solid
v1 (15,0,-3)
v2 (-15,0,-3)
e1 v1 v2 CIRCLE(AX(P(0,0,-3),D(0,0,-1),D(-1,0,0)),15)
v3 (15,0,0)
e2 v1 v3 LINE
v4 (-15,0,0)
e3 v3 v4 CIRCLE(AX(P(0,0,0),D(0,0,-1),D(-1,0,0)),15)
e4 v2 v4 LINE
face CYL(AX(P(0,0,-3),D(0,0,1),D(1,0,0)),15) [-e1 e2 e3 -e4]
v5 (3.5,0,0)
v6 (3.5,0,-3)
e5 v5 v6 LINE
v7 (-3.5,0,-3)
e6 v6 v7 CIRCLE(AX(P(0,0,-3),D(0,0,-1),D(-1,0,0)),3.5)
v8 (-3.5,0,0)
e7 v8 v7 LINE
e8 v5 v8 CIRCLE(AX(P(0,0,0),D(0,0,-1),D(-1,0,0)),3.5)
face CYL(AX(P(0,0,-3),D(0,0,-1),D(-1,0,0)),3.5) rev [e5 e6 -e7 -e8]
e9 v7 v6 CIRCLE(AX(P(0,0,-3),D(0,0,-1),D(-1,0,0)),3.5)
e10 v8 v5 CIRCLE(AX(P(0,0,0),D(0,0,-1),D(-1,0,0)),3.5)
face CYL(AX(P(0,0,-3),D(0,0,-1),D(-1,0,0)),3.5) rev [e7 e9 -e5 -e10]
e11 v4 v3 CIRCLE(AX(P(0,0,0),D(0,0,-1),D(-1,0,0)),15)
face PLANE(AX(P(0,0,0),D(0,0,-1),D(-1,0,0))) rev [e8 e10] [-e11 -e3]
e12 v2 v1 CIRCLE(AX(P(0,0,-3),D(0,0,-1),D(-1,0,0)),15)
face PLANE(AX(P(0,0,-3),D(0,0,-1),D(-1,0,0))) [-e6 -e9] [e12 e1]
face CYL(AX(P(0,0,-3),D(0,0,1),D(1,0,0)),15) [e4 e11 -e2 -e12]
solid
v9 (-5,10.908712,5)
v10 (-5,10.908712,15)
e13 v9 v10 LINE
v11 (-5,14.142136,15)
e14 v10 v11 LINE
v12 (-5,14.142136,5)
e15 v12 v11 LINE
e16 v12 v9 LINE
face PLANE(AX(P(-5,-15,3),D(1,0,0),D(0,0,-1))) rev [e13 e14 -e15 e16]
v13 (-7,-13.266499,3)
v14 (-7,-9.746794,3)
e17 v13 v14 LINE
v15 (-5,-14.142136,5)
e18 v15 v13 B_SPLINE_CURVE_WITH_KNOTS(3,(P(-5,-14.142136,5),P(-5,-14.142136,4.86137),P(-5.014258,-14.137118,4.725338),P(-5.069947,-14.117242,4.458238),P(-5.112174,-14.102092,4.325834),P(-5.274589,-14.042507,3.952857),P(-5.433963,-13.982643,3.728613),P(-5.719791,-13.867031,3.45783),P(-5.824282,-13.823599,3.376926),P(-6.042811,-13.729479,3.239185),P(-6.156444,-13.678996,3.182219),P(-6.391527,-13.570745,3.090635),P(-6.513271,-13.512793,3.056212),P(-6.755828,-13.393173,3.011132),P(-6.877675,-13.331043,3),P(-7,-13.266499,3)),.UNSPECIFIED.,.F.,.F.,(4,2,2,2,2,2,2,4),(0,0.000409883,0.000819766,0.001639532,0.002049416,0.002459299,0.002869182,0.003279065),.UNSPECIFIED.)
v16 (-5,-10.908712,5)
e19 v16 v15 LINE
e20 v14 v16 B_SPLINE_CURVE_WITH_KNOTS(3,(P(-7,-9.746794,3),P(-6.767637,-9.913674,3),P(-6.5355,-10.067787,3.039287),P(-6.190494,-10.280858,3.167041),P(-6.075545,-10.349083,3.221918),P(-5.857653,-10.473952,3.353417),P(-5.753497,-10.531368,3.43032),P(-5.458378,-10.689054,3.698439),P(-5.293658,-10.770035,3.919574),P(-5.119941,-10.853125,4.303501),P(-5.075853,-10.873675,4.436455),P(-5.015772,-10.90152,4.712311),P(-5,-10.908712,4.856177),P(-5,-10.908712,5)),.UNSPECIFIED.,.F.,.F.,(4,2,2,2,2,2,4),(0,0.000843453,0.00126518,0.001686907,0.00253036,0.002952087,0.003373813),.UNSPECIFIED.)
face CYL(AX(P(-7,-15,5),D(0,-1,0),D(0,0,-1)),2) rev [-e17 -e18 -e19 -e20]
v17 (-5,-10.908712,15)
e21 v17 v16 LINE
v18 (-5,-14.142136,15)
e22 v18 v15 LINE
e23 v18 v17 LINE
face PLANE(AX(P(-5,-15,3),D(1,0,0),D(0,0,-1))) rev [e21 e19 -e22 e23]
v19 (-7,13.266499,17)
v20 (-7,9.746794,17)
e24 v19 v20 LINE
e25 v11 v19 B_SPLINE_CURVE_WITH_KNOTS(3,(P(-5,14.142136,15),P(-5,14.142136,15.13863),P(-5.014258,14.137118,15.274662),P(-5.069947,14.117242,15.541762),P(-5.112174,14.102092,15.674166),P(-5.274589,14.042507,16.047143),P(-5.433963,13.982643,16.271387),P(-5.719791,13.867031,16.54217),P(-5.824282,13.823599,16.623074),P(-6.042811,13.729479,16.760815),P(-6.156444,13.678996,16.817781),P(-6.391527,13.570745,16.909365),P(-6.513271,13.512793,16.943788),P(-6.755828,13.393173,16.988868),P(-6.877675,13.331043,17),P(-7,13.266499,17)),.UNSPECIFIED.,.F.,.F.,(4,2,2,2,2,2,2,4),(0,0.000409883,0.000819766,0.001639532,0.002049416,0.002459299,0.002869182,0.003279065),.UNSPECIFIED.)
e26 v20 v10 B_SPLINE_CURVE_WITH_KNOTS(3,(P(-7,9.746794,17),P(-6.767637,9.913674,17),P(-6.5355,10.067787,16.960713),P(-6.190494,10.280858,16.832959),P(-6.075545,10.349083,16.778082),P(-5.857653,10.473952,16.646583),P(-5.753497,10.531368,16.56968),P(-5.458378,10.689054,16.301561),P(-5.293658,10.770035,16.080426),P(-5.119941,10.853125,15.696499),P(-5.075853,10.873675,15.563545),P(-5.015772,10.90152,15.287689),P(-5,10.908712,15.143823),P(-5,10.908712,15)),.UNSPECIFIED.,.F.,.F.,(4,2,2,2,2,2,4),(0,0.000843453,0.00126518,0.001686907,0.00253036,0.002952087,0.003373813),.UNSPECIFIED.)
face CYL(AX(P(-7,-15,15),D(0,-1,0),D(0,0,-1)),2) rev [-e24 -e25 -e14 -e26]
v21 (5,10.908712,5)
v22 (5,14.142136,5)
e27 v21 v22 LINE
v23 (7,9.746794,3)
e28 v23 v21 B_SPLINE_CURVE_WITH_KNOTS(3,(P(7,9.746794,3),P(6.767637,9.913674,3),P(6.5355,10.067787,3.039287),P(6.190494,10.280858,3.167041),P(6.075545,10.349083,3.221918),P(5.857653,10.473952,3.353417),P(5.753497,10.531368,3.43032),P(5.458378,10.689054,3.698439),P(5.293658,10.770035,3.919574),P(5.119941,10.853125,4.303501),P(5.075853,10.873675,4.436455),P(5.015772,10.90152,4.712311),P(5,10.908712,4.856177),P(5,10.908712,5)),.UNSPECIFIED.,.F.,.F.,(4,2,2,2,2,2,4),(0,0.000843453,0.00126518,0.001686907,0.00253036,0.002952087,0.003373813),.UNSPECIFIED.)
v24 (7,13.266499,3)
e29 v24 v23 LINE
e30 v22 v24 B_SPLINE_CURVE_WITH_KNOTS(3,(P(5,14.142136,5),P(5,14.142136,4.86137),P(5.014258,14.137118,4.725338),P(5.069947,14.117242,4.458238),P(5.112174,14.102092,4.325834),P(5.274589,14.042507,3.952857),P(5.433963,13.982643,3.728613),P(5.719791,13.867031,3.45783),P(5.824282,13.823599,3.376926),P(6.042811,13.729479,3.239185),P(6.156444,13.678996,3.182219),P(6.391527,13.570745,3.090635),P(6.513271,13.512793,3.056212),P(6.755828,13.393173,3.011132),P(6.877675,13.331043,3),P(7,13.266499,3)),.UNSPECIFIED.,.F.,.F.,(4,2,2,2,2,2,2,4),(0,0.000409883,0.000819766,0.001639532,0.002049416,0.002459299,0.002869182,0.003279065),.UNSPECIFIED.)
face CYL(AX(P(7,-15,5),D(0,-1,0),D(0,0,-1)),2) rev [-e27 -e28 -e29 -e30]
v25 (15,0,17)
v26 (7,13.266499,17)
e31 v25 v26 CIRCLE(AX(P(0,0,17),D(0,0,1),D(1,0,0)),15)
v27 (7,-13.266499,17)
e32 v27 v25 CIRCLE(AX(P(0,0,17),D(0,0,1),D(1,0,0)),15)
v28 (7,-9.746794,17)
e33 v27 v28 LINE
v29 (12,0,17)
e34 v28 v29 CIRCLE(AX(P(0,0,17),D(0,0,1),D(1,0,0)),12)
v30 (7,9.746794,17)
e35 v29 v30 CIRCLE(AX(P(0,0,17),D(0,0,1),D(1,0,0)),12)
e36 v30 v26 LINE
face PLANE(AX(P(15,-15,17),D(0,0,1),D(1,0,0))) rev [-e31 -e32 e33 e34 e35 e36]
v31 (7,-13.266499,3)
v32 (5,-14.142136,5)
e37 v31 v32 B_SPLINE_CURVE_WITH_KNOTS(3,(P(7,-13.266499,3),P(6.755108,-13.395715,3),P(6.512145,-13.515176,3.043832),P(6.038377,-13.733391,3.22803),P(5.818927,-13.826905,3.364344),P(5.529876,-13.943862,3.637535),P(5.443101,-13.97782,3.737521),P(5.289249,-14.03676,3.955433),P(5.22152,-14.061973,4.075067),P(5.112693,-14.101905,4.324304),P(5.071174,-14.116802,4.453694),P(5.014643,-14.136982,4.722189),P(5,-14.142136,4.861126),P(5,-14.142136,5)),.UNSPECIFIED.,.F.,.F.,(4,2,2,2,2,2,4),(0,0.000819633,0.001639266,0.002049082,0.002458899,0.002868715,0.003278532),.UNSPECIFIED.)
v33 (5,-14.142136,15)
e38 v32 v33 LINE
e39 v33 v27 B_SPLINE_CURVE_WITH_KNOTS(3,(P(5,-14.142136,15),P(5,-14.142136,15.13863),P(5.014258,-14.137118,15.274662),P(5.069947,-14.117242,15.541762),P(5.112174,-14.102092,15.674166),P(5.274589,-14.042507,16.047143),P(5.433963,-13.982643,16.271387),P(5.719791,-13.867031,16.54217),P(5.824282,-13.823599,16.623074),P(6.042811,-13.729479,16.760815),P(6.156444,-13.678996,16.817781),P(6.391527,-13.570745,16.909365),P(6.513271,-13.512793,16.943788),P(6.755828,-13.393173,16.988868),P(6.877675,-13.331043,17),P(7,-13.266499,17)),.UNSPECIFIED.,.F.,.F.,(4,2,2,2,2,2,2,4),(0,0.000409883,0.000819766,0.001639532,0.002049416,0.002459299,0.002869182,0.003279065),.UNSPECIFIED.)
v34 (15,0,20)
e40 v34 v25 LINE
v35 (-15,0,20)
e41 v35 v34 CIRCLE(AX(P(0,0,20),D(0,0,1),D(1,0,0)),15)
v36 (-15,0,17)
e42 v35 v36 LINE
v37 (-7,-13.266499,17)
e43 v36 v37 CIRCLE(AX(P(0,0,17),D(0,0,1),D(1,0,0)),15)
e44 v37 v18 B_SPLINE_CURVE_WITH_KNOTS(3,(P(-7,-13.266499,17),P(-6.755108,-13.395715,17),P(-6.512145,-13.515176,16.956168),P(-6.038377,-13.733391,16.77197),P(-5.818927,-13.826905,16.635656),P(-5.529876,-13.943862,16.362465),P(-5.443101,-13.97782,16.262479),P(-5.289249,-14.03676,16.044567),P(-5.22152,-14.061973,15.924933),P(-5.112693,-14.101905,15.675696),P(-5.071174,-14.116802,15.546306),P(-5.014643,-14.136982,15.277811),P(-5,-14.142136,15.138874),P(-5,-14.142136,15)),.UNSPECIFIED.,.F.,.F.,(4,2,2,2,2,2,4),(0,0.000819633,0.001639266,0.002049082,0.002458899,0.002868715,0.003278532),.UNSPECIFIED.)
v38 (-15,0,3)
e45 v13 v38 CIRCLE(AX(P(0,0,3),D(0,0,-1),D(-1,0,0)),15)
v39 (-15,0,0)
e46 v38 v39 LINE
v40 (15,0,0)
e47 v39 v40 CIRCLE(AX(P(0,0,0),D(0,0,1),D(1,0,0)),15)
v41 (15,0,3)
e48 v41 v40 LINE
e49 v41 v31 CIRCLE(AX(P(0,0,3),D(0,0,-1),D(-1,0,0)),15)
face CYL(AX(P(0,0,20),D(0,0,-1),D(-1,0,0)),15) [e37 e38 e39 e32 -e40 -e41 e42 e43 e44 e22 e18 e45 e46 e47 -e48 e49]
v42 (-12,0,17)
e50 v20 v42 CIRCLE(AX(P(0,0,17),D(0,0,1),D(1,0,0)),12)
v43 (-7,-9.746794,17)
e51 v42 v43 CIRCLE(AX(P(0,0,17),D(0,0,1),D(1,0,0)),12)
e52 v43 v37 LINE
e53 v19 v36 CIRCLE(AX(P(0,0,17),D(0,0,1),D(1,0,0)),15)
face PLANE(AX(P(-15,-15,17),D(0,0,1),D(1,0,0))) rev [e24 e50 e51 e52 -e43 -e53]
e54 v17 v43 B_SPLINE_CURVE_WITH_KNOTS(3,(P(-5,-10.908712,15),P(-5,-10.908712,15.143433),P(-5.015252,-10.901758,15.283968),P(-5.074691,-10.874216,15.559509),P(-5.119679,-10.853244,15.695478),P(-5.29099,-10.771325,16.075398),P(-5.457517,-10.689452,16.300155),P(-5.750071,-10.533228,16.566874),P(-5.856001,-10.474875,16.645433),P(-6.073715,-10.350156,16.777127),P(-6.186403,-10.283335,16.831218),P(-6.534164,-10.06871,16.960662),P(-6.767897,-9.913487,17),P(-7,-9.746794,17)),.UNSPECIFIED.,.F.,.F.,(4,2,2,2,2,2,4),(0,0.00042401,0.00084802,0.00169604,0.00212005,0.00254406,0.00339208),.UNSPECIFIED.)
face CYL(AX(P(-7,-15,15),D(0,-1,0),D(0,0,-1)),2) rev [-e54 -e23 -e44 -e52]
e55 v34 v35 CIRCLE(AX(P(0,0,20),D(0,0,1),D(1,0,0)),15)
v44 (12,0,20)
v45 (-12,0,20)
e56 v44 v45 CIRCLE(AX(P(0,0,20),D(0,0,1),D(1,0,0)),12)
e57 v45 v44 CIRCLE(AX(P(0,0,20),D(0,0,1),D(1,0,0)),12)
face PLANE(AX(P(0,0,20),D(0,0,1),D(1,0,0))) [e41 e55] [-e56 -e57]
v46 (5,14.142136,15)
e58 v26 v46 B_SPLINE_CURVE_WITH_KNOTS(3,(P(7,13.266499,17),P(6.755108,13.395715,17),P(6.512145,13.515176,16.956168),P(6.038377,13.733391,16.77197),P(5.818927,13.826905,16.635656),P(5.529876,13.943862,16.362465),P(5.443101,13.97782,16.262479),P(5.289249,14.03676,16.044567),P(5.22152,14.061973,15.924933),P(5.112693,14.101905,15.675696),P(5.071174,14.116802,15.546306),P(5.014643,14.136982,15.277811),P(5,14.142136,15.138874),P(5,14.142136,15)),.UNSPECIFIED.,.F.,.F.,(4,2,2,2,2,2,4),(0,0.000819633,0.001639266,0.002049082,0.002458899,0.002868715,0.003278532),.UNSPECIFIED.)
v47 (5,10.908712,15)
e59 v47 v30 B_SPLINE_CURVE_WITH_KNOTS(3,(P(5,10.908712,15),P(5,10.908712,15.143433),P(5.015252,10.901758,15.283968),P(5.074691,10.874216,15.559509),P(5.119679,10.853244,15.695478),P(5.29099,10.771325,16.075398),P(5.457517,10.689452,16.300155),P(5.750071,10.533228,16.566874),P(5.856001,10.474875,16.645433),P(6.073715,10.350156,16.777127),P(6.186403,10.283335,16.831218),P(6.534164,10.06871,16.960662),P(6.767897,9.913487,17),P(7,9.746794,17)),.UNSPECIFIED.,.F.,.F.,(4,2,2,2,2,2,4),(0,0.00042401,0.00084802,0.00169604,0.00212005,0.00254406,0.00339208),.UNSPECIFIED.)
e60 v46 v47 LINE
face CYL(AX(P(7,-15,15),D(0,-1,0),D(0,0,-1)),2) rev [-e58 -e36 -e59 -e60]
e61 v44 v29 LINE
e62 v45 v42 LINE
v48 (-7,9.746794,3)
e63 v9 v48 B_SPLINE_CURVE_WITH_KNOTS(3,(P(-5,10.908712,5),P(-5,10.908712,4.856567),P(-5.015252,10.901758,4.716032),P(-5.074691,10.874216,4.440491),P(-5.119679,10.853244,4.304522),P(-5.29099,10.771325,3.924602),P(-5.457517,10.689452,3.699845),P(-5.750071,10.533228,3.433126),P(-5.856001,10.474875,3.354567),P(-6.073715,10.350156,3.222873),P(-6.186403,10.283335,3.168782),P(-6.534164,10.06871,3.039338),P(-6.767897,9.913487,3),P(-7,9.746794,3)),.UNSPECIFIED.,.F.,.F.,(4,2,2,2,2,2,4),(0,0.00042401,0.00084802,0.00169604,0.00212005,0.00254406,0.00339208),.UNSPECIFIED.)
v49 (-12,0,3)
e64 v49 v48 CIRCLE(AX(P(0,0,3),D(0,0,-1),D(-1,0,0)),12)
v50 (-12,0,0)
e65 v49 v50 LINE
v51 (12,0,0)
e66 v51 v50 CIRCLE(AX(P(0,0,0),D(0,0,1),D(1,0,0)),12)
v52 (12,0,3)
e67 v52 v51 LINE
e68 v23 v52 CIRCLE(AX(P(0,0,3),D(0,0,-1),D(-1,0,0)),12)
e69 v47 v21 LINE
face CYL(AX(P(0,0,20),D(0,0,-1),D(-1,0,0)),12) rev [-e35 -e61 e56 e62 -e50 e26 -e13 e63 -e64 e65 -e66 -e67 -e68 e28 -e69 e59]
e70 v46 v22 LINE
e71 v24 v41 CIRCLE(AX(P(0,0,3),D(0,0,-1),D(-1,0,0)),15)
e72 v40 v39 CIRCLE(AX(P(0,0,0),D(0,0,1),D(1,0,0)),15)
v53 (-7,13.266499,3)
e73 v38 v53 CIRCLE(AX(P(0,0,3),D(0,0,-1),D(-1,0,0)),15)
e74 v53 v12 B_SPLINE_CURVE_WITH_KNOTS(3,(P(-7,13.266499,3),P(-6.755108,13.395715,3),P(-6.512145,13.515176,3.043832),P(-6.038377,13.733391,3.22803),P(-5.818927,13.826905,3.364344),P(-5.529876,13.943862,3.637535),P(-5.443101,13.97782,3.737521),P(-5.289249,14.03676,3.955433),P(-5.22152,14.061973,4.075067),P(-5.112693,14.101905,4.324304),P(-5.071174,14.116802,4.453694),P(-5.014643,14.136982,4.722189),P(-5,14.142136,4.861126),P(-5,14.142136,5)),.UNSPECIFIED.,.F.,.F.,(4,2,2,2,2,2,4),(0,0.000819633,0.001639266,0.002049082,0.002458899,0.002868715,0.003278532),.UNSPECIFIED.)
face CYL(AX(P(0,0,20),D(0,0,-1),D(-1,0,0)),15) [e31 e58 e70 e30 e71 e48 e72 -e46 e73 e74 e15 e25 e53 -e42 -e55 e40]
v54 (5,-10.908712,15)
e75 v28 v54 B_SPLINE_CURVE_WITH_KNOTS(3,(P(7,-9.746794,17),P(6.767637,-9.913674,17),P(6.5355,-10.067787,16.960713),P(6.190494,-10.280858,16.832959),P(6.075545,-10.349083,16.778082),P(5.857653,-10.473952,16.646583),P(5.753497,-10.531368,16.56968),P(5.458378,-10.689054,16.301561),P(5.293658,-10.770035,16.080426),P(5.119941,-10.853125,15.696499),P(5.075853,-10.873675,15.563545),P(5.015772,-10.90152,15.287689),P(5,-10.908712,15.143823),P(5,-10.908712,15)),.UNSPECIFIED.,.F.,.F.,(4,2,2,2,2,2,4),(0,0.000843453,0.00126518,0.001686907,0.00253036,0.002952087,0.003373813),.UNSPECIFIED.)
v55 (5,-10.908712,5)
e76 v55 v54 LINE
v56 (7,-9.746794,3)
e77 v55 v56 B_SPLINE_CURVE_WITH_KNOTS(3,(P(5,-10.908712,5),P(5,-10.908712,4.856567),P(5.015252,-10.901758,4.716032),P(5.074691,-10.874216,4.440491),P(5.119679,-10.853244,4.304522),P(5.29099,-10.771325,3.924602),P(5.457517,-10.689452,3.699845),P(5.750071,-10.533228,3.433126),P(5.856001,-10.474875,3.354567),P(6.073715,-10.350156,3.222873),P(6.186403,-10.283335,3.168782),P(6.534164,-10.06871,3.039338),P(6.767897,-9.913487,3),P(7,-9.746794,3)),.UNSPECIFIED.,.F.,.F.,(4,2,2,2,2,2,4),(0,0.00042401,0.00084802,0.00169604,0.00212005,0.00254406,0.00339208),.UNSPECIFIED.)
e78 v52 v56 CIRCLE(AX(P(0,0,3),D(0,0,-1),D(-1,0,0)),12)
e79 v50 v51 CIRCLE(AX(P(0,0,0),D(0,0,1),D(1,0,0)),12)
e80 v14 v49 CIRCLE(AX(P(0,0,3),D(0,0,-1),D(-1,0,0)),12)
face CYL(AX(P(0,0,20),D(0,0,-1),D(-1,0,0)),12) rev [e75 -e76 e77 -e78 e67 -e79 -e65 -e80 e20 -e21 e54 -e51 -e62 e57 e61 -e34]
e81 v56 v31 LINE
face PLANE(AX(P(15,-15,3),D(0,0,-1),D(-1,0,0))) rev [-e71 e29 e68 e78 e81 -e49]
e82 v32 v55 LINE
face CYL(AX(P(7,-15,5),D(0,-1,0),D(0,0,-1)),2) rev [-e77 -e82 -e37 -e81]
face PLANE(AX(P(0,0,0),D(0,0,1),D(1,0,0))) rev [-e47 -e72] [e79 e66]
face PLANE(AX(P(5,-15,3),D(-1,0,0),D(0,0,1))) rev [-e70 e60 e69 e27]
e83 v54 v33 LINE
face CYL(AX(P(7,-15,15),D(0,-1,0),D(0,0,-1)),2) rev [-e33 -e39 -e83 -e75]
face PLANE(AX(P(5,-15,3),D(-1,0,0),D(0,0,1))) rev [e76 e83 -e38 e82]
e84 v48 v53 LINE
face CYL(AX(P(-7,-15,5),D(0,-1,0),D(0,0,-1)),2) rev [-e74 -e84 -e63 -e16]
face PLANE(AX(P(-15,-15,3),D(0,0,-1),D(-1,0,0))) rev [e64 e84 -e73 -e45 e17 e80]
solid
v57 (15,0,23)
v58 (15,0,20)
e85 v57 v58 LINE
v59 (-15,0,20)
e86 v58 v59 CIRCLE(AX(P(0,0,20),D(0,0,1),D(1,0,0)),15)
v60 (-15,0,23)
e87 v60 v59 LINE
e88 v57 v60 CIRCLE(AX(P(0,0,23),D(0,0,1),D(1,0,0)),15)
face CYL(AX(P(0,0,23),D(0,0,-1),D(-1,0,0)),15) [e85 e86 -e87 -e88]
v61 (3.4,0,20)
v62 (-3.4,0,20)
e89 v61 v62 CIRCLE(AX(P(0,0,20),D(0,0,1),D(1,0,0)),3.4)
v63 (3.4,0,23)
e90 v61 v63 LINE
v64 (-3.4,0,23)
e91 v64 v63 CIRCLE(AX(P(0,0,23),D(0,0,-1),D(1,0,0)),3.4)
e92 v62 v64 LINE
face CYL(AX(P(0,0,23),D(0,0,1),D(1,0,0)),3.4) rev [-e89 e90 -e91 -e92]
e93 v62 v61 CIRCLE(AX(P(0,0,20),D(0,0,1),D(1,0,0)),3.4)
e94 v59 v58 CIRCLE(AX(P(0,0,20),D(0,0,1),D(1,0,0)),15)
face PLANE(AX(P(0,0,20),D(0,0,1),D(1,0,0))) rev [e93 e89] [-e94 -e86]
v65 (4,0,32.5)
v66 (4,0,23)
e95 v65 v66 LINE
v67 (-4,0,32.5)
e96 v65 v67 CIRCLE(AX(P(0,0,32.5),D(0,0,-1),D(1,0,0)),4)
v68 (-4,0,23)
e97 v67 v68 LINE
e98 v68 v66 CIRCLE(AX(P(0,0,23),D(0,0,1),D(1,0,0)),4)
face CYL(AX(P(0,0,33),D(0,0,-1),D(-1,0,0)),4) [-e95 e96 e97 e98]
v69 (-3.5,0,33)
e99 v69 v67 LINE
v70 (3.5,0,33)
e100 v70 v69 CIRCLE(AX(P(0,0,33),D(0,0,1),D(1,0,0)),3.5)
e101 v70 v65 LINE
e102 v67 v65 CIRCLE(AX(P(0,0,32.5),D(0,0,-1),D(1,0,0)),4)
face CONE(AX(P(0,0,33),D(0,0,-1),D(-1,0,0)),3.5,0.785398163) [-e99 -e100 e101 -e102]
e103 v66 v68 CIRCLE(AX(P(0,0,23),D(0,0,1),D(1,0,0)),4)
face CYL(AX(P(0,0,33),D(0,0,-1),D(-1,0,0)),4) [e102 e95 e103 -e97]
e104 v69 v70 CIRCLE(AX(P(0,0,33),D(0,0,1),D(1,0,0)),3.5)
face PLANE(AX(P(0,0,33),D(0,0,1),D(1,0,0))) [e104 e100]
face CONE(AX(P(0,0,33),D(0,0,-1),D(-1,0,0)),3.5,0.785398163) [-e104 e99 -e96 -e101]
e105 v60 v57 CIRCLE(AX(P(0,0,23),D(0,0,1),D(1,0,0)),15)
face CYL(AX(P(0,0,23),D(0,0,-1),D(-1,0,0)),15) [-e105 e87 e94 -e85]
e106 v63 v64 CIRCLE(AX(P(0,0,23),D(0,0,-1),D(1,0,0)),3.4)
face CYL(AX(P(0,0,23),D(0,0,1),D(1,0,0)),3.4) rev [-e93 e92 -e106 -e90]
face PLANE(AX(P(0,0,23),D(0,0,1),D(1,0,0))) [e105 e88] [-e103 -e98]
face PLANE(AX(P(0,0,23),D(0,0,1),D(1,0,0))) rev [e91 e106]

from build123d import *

# Parameters (mm, degrees)
SKETCH1_R               = 15
SKETCH1_R_2             = 12
BOSS_EXTRUDE1_DEPTH     = 20
CUT_EXTRUDE1_DEPTH      = 30.154759474
CUT_EXTRUDE1_DEPTH_BACK = 30.154759474
SKETCH2_W               = 10
SKETCH2_H               = 14
SKETCH3_R               = 15
BOSS_EXTRUDE2_DEPTH     = 3
SKETCH5_R               = 15
BOSS_EXTRUDE3_DEPTH     = 3
SKETCH11_R              = 4
BOSS_EXTRUDE4_DEPTH     = 10
FILLET1_R               = 2
CHAMFER1_SIZE           = 0.5


with BuildPart() as part:
    # Sketch1 → Boss-Extrude1 (new body)
    with BuildSketch(Plane.XY):
        Circle(SKETCH1_R)
        Circle(SKETCH1_R_2, mode=Mode.SUBTRACT)
    extrude(amount=BOSS_EXTRUDE1_DEPTH)

    # Sketch2 → Cut-Extrude1 (cut, two sides: drawn at the far end of the back side and taken through both)
    with BuildSketch(Plane(origin=(0, 0, 0), x_dir=(1, 0, 0), z_dir=(0, 1, 0)).offset(-CUT_EXTRUDE1_DEPTH_BACK)):
        with Locations((-10, -10)):
            Rectangle(SKETCH2_W, SKETCH2_H)
        with Locations((10, -10)):
            Rectangle(SKETCH2_W, SKETCH2_H)
    extrude(amount=CUT_EXTRUDE1_DEPTH + CUT_EXTRUDE1_DEPTH_BACK, mode=Mode.SUBTRACT)

    # Fillet1
    fillet1_edges = [part.edges().sort_by_distance(p)[0] for p in [
        (-5, -12.525423869, 3),
        (-5, 12.525423869, 3),
        (-5, 12.525423869, 17),
        (-5, -12.525423869, 17),
        (5, 12.525423869, 3),
        (5, -12.525423869, 3),
        (5, 12.525423869, 17),
        (5, -12.525423869, 17),
    ]]
    fillet(fillet1_edges, radius=FILLET1_R)


with BuildPart() as body_2:
    # Sketch3 → Boss-Extrude2 (new body)
    with BuildSketch(Plane.XY.offset(20)):
        Circle(SKETCH3_R)
    extrude(amount=BOSS_EXTRUDE2_DEPTH)

    # Sketch10 → M8 Tapped Hole1 (revolve, cut)
    with BuildSketch(Plane(origin=(0, 0, 23), x_dir=(0, -1, 0), z_dir=(1, 0, 0))):
        Polygon((0, 0), (0, 12.042926105), (3.4, 10), (3.4, 0), align=None)
    revolve(axis=Axis((0, 0, 29.35), (0, 0, -1)), mode=Mode.SUBTRACT)

    # Sketch11 → Boss-Extrude4 (add)
    with BuildSketch(Plane.XY.offset(23)):
        Circle(SKETCH11_R)
    extrude(amount=BOSS_EXTRUDE4_DEPTH)

    # Chamfer1
    chamfer1_edges = [body_2.edges().sort_by_distance(p)[0] for p in [
        (-4, 0, 33),
    ]]
    chamfer(chamfer1_edges, length=CHAMFER1_SIZE)


with BuildPart() as body_3:
    # Sketch5 → Boss-Extrude3 (new body)
    with BuildSketch(Plane(origin=(0, 0, 0), x_dir=(-1, 0, 0), z_dir=(0, 0, -1))):
        Circle(SKETCH5_R)
    extrude(amount=BOSS_EXTRUDE3_DEPTH)

    # Sketch8 → M6 Clearance Hole1 (revolve, cut)
    with BuildSketch(Plane(origin=(0, 0, -3), x_dir=(0, 1, 0), z_dir=(1, 0, 0))):
        Polygon((0, 0), (0, 7.103012167), (3.5, 5), (3.5, 0), align=None)
    revolve(axis=Axis((0, 0, -9.35), (0, 0, 1)), mode=Mode.SUBTRACT)


solid = Compound([part.part, body_2.part, body_3.part])
